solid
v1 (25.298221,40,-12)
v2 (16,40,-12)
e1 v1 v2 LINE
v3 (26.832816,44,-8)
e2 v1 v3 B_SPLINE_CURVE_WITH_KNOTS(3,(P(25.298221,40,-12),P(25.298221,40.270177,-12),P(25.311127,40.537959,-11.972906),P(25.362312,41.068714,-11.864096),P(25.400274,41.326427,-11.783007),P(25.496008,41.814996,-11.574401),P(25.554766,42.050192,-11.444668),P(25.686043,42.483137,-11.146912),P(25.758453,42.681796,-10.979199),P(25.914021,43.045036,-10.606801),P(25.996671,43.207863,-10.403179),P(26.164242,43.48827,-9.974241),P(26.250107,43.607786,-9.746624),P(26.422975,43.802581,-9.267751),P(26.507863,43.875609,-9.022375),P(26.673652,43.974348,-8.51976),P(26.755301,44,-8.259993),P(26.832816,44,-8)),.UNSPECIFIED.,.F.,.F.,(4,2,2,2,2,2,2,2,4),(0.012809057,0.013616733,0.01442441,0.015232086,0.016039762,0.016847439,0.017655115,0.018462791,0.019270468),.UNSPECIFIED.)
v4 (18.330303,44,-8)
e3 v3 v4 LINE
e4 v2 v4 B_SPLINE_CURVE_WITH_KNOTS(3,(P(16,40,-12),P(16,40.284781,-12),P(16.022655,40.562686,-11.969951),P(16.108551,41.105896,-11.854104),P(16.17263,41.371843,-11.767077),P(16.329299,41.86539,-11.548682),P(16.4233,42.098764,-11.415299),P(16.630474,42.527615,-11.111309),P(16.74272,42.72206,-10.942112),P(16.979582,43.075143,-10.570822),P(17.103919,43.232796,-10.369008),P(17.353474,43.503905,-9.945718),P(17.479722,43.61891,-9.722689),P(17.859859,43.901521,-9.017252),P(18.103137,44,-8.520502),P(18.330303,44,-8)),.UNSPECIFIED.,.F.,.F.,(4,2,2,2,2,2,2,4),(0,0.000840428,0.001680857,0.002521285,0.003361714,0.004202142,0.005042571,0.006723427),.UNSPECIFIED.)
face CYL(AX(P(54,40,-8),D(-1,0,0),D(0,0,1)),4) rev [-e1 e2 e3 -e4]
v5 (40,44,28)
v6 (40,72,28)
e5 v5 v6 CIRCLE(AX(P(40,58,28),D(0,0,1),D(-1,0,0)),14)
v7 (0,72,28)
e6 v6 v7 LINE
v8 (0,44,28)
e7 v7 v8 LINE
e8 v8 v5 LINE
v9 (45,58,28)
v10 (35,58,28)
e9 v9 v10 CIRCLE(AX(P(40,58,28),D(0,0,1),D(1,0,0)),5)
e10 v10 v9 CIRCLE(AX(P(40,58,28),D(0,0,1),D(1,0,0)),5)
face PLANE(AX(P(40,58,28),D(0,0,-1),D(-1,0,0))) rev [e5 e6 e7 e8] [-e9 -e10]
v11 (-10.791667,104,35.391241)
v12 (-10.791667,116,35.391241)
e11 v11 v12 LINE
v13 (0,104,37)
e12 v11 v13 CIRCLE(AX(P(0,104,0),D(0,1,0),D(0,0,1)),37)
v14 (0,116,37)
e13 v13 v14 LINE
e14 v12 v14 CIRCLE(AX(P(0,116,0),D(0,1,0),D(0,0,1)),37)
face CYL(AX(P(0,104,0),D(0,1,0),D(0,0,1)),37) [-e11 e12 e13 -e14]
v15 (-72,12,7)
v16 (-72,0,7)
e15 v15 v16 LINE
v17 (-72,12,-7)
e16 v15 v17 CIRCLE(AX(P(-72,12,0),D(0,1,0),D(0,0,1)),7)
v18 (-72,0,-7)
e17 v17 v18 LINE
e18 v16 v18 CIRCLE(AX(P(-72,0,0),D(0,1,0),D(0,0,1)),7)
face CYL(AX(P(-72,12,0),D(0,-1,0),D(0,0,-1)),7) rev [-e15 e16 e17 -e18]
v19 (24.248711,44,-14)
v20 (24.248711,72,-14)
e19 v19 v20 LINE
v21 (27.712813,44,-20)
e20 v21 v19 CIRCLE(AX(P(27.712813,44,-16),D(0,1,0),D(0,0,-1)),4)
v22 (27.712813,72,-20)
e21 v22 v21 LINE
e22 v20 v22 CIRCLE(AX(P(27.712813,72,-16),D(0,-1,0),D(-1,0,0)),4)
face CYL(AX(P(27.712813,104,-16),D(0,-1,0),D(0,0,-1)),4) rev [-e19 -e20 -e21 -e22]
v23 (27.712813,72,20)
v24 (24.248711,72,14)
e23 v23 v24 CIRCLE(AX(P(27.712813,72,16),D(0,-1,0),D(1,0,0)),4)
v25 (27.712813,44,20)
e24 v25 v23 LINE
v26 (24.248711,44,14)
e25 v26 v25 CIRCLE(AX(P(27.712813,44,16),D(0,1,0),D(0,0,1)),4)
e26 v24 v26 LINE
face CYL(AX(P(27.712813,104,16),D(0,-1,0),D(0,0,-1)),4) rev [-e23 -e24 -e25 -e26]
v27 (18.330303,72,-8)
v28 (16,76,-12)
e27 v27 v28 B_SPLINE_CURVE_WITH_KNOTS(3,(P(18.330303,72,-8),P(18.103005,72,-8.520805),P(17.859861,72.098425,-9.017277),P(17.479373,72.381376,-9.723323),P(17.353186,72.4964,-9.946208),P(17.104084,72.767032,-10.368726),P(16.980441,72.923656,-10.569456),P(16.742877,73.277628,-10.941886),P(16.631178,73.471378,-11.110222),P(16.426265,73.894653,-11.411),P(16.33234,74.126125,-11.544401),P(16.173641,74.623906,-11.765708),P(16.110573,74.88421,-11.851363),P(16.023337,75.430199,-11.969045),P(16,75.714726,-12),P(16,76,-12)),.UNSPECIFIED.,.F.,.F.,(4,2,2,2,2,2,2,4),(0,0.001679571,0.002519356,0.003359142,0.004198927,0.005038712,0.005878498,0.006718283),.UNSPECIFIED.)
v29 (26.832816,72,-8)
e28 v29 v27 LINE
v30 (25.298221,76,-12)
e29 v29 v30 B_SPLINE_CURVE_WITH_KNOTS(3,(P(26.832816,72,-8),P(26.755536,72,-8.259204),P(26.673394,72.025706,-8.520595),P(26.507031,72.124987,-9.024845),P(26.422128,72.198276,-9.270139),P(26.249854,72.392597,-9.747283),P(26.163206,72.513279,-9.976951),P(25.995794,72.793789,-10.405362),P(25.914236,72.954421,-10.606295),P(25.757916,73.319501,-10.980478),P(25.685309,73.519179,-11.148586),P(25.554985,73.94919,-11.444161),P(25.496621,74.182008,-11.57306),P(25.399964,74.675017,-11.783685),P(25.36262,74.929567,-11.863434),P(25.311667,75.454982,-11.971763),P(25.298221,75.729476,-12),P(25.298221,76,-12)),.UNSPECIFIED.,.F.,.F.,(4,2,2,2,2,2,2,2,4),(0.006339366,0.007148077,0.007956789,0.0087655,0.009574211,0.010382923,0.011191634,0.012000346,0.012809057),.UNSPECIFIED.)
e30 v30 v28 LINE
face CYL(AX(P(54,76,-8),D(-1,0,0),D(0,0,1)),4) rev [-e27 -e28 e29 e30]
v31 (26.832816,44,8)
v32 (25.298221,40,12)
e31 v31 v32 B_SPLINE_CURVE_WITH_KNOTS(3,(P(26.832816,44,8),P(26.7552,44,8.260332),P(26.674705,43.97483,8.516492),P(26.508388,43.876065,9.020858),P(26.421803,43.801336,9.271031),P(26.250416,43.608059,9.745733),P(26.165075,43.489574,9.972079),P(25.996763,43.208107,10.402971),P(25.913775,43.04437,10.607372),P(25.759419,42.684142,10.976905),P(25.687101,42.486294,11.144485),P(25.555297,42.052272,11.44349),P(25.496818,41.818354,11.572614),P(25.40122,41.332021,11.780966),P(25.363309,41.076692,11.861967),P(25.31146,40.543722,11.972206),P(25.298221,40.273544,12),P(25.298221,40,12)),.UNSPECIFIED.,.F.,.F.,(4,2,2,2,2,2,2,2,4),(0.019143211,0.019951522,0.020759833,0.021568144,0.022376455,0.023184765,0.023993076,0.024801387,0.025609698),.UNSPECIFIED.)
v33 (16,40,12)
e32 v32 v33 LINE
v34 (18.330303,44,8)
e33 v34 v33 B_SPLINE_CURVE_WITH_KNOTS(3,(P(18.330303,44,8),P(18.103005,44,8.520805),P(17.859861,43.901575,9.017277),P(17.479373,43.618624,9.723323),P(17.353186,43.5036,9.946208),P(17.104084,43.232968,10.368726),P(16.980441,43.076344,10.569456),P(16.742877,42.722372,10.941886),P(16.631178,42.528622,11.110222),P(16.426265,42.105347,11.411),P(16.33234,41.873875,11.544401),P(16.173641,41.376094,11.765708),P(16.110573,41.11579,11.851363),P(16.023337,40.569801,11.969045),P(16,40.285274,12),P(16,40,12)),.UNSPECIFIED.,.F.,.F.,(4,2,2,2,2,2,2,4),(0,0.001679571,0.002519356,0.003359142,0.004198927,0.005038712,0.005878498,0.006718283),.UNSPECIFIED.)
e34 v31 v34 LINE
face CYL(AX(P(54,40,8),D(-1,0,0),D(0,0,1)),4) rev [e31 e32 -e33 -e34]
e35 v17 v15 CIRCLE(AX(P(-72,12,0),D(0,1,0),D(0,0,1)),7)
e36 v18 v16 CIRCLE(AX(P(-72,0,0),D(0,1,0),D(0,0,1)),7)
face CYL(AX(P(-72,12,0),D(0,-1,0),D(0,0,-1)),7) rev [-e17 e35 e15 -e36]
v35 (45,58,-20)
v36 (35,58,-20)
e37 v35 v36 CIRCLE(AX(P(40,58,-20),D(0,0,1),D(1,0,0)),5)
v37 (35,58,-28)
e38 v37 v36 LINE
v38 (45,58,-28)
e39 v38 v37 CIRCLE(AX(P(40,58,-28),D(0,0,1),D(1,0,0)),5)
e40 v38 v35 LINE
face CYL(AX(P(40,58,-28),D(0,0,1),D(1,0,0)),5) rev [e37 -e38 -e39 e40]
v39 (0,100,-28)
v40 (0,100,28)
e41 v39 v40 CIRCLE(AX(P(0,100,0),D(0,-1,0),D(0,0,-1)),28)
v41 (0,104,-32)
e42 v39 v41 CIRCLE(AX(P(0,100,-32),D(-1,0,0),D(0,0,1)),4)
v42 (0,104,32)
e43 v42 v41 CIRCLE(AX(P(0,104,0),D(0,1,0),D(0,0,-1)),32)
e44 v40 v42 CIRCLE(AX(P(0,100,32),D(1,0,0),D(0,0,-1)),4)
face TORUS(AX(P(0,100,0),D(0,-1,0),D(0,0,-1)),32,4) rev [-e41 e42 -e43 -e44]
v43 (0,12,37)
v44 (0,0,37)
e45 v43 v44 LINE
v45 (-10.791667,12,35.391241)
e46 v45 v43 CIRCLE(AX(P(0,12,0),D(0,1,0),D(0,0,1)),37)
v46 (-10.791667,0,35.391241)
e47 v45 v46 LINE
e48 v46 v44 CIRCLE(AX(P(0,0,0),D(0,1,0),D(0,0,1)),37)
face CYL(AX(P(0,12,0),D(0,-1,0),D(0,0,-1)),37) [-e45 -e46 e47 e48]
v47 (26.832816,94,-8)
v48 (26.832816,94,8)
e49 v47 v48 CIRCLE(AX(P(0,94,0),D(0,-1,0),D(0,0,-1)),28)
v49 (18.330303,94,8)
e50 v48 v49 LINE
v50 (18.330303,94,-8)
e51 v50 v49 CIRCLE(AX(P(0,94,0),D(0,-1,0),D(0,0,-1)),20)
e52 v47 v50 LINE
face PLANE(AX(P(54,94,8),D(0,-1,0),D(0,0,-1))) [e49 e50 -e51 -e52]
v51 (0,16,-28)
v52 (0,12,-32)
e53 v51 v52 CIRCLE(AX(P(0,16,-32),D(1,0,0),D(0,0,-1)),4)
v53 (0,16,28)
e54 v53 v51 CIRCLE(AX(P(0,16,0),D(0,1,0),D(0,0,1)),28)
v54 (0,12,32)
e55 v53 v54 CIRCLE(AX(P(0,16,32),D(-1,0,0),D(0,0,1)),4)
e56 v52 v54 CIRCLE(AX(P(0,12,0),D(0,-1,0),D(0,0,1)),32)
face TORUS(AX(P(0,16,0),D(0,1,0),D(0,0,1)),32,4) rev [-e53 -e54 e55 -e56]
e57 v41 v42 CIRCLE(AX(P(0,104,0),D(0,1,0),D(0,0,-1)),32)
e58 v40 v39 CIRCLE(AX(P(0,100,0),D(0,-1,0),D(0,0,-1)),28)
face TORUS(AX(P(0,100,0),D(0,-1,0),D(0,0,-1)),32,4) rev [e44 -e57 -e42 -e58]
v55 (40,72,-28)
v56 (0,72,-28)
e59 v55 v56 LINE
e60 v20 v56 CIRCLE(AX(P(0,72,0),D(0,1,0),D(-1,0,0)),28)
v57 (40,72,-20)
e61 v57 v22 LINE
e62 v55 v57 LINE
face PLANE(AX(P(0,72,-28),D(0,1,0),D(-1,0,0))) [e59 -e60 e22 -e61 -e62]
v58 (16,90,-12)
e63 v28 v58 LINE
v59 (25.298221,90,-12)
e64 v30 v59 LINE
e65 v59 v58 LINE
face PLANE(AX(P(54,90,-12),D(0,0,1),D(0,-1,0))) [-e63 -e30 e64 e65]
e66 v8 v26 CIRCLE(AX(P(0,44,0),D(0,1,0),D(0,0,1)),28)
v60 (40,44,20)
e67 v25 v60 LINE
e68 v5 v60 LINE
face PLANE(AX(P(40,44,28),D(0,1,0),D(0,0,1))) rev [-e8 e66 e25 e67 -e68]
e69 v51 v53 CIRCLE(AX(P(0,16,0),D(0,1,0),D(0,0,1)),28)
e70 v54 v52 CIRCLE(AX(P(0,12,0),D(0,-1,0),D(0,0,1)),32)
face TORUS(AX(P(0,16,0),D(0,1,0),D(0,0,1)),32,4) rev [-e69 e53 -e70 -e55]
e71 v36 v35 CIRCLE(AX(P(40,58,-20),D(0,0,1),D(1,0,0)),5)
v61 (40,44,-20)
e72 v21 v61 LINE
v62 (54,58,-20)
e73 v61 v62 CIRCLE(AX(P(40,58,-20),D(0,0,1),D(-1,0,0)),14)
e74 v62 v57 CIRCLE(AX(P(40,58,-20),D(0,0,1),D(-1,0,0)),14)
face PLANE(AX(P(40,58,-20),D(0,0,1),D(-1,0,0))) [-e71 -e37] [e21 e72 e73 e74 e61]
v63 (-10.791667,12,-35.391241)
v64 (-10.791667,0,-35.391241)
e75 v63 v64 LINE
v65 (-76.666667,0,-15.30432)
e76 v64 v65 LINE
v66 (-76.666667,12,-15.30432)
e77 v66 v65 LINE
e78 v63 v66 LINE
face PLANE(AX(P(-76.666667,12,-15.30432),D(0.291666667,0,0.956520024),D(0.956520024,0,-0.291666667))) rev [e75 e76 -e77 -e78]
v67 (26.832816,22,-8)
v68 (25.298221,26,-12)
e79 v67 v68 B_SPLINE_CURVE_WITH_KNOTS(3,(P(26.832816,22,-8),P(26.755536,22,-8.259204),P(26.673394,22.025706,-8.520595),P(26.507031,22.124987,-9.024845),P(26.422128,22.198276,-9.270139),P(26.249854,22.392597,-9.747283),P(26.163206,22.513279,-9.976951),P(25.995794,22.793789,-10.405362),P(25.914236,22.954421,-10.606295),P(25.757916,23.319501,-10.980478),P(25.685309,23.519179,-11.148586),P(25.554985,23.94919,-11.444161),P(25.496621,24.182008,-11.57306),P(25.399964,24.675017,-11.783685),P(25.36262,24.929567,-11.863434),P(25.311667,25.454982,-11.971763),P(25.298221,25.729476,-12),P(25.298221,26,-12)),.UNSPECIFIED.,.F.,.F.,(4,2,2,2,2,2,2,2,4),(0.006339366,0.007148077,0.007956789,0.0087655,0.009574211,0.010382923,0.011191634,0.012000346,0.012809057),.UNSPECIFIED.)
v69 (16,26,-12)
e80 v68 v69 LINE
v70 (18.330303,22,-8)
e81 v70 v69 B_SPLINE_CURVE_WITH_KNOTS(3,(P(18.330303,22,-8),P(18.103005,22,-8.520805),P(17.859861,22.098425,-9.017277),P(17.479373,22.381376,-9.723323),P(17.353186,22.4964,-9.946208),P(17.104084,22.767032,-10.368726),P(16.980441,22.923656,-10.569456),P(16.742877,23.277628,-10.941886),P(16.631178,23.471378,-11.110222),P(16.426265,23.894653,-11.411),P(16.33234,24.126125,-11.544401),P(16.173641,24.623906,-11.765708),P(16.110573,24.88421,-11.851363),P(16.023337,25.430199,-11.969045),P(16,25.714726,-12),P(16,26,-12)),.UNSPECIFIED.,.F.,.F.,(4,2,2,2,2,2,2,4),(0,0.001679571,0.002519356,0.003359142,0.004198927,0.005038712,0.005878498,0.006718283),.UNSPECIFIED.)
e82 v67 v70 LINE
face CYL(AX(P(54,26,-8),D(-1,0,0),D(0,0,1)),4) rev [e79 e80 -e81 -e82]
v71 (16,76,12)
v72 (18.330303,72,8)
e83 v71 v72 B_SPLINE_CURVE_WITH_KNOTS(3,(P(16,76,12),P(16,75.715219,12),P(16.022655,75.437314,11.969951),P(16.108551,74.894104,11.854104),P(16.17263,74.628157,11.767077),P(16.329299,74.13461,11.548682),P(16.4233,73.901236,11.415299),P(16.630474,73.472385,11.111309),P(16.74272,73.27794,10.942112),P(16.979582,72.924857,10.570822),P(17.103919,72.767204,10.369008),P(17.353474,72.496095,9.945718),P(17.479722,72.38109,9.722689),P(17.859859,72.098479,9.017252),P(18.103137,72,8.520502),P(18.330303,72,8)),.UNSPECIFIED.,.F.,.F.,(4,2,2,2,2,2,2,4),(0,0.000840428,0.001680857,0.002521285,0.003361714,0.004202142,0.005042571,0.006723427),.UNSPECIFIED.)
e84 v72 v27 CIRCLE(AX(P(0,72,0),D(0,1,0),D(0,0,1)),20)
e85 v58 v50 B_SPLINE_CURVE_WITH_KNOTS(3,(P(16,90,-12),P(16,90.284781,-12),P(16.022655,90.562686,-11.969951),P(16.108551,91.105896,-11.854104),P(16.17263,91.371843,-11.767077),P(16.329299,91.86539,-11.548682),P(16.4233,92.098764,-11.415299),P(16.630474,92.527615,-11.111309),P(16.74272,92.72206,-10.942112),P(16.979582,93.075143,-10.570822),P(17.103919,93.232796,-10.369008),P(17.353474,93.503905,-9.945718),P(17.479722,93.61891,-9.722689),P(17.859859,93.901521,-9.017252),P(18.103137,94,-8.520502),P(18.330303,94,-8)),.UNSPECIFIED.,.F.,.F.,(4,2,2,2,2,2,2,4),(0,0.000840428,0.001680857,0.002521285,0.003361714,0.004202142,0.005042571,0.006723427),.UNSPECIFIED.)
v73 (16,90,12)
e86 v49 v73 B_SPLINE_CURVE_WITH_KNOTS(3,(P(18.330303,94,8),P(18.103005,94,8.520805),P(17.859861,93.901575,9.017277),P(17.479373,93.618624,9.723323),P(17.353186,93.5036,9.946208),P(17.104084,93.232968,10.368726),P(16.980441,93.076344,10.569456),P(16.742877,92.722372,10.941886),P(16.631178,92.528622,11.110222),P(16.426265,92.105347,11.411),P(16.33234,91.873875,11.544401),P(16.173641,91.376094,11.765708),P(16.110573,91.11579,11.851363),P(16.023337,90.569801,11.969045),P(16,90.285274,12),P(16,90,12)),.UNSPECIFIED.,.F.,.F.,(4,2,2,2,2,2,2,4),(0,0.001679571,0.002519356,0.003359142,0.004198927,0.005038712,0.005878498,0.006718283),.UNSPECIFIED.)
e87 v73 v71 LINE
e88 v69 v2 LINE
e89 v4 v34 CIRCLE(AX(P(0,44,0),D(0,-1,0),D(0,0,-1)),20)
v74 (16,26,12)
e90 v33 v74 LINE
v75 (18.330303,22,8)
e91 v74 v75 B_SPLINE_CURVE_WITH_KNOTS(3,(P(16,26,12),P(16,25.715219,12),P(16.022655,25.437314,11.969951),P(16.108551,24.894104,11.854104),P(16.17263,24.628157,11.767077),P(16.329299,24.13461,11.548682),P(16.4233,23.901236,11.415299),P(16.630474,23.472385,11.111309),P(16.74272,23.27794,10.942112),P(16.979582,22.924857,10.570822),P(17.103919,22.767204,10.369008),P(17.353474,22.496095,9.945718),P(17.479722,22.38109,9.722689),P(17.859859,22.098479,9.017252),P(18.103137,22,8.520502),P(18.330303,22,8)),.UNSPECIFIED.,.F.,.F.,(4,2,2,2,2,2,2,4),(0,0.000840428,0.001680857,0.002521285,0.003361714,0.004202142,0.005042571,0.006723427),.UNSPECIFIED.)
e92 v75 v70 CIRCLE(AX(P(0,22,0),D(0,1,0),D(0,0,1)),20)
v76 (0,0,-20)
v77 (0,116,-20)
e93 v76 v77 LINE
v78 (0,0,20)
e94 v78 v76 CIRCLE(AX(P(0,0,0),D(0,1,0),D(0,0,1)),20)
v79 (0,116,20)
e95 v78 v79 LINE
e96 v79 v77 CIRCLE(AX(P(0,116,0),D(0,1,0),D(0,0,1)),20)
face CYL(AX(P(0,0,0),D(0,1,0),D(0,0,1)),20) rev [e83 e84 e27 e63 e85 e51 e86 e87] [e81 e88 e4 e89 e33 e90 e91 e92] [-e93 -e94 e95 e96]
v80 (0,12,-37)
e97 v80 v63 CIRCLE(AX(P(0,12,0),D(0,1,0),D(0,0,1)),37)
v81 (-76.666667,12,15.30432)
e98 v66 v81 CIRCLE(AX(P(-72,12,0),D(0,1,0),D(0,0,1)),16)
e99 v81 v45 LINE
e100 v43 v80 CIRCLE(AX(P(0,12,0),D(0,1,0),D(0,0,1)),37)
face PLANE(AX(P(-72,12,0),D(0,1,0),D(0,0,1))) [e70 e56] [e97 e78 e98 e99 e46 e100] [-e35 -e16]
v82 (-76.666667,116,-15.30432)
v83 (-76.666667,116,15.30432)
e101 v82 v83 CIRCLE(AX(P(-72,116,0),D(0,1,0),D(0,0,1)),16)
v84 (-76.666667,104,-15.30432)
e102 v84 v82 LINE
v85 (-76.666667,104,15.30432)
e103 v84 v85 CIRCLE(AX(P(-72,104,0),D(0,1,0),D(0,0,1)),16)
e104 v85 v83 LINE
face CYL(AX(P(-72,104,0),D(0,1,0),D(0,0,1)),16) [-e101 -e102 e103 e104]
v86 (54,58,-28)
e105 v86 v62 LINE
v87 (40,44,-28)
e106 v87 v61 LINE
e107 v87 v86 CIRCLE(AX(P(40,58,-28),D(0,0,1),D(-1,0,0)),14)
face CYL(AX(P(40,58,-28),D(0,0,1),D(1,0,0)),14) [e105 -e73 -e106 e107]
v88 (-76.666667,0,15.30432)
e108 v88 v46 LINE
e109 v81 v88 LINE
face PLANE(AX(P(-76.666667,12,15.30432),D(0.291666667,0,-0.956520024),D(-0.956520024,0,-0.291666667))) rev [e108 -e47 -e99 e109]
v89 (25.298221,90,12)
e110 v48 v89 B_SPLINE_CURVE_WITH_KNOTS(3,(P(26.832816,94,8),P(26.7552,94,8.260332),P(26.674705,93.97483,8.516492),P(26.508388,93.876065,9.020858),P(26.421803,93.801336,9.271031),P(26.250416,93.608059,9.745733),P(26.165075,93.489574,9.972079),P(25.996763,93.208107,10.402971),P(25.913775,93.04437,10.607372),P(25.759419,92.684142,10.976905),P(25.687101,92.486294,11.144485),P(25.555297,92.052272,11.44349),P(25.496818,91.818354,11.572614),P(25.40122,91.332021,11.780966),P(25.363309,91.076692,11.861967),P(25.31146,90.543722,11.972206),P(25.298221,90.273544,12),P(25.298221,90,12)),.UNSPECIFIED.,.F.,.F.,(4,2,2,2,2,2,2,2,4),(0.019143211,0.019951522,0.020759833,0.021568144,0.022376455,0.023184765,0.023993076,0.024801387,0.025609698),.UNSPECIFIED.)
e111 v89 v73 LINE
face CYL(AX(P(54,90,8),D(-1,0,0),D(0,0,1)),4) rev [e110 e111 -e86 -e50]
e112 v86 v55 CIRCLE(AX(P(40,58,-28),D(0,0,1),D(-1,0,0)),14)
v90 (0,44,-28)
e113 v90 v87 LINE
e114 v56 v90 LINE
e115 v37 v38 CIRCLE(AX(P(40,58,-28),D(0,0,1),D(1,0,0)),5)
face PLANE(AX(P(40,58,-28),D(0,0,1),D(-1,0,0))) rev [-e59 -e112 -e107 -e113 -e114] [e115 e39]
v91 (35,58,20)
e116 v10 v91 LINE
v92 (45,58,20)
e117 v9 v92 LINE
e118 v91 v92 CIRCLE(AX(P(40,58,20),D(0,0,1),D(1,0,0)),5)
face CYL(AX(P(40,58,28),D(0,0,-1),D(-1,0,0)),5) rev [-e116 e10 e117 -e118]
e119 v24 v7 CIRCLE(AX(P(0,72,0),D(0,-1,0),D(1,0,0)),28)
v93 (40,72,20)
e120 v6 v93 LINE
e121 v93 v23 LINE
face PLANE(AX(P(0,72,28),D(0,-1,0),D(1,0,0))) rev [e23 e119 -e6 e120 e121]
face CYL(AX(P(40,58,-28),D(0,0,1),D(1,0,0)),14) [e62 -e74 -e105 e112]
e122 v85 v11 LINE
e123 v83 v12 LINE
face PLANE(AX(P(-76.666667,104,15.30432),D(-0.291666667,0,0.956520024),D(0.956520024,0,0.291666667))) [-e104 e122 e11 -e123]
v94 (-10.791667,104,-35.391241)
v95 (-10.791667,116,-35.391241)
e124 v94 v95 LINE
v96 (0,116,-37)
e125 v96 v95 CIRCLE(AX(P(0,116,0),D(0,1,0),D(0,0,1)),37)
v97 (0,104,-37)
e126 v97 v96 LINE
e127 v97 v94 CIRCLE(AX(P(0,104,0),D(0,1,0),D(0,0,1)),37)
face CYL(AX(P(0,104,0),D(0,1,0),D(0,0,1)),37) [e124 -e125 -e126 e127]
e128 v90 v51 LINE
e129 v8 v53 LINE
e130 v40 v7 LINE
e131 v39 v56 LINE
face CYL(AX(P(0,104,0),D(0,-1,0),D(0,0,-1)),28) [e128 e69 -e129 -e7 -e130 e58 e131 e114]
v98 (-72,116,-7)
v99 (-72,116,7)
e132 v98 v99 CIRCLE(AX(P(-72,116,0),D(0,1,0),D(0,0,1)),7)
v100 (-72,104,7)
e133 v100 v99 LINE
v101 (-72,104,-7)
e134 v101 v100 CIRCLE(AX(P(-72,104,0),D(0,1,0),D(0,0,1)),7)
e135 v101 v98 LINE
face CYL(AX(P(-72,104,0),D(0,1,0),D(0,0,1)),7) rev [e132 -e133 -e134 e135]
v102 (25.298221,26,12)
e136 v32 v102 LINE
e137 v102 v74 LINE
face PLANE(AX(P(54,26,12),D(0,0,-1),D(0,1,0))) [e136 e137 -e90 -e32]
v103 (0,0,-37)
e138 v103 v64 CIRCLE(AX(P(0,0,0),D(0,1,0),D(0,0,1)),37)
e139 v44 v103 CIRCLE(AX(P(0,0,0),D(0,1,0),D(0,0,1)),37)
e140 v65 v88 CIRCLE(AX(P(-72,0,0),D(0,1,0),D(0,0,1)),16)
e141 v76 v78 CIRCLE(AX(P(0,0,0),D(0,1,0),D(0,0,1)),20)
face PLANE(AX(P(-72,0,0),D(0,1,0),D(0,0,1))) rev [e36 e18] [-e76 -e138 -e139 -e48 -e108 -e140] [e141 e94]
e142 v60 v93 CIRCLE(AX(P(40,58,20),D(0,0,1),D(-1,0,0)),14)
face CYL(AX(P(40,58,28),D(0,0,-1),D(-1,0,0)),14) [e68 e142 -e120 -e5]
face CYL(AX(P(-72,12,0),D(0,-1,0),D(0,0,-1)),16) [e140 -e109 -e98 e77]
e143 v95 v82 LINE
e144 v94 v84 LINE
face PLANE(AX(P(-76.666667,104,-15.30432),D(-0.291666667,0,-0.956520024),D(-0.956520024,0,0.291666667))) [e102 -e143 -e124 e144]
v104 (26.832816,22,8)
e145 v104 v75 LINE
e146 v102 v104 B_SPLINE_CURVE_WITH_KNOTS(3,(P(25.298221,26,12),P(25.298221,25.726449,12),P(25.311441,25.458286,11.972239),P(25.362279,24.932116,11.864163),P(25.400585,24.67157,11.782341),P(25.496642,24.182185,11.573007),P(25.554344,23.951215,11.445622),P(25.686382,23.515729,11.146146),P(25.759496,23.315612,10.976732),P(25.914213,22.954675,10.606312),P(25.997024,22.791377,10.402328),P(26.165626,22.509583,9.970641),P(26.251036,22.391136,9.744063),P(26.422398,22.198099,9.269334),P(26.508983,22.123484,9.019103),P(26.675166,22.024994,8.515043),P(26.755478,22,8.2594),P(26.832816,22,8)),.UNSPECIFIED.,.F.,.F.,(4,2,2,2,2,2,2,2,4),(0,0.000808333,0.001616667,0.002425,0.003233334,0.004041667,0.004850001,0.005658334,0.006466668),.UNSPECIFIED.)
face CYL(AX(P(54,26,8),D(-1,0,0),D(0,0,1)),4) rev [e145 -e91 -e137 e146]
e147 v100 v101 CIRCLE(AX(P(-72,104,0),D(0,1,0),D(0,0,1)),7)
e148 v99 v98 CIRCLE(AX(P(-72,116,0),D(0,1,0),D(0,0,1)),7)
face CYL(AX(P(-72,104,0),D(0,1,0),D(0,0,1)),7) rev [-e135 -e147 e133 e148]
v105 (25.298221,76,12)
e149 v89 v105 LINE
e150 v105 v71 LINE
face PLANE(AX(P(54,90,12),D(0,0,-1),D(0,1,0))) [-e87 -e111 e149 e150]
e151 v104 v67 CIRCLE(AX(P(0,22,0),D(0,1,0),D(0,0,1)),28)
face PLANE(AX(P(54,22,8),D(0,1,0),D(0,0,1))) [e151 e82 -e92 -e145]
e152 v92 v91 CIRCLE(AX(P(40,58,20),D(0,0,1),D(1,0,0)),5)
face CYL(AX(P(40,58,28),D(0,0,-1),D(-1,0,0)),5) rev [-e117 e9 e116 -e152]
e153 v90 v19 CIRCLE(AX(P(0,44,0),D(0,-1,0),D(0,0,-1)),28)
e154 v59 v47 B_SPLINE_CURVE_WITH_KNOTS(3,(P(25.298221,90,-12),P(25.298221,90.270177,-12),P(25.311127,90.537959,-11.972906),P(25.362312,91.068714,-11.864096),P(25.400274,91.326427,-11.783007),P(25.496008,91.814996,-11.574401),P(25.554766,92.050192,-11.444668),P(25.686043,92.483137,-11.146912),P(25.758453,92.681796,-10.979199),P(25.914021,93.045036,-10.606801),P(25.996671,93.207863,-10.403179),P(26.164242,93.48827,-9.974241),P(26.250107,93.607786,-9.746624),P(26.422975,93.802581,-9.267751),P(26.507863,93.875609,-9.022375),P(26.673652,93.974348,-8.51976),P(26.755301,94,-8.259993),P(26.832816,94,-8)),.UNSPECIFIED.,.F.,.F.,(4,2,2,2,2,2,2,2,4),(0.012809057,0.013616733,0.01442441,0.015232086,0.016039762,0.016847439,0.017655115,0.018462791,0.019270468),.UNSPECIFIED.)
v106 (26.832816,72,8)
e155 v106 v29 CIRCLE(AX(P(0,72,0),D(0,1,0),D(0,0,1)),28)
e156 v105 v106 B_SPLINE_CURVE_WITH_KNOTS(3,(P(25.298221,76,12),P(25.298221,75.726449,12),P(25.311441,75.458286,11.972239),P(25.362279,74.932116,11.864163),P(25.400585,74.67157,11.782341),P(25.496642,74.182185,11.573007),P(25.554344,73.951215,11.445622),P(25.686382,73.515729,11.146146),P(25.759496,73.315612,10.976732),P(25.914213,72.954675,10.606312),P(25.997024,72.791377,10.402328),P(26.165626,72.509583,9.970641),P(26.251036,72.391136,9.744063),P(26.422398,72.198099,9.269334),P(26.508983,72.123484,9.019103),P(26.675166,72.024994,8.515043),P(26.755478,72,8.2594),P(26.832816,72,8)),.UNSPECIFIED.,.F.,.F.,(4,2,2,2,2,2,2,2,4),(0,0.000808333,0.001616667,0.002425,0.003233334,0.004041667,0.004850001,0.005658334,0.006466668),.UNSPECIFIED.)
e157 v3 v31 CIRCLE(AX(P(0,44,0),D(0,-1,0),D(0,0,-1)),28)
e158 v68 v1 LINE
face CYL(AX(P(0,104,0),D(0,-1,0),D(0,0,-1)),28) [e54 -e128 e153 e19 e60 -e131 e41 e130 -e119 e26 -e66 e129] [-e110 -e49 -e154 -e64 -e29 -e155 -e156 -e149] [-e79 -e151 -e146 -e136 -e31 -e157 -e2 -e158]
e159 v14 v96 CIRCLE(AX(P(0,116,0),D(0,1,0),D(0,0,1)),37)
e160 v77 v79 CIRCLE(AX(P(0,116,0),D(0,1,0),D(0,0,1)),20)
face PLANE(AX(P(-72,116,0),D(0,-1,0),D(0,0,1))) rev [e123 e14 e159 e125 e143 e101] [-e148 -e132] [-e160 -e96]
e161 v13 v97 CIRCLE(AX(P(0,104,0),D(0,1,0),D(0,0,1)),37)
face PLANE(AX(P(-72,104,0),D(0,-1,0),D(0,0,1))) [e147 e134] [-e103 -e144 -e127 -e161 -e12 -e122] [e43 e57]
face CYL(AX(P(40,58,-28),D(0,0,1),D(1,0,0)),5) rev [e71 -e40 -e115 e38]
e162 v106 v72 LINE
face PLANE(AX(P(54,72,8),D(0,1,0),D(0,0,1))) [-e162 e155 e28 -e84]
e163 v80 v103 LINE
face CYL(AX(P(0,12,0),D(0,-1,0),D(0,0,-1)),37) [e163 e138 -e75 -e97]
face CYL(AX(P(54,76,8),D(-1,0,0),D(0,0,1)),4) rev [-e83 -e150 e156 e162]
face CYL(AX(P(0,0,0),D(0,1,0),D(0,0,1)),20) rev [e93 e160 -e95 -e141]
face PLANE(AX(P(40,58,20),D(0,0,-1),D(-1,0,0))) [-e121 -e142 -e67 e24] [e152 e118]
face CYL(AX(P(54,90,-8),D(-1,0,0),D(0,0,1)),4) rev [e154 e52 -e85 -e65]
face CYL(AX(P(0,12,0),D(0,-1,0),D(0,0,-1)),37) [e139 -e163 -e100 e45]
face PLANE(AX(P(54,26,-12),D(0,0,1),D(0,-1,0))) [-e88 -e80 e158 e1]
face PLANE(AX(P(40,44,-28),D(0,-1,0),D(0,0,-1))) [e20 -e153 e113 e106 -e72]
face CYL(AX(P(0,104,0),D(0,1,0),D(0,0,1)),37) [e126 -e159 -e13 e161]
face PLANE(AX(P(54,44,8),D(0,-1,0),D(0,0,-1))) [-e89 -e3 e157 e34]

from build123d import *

# Parameters (mm, degrees)
LOWER_ARM_PROFILE_R    = 7
LOWER_ARM_PLATE_DEPTH  = 12
SLEEVE_PROFILE_56_R    = 28
SLEEVE_56_DEPTH        = 92
ARM_FILLETS_R4_R       = 4
TRUNNION_START         = 20
TRUNNION_LUG_PROFILE_R = 5
TRUNNION_LUG_DEPTH     = 8
LUG_FILLETS_R4_R       = 4
SLEEVE_WINDOWS_DEPTH   = 151.229823937
BORE_PROFILE_40_R      = 20
BORE_40_DEPTH          = 151.229823937


with BuildPart() as part:
    # Lower Arm Profile → Lower Arm Plate (new body)
    with BuildSketch(Plane(origin=(0, 0, 0), x_dir=(1, 0, 0), z_dir=(0, 1, 0))):
        with BuildLine():
            Line((-76.666666667, 15.304320378), (-10.791666667, 35.391240873))
            ThreePointArc((-10.791666667, 35.391240873), (37, 0), (-10.791666667, -35.391240873))
            Line((-10.791666667, -35.391240873), (-76.666666667, -15.304320378))
            ThreePointArc((-76.666666667, -15.304320378), (-88, 0), (-76.666666667, 15.304320378))
        make_face()
        with Locations(Location((-72, 0, 0), (0, 0, 270))):
            Circle(LOWER_ARM_PROFILE_R, mode=Mode.SUBTRACT)
    lower_arm_plate = extrude(amount=LOWER_ARM_PLATE_DEPTH)

    # Sleeve Profile Ø56 → Sleeve Ø56 (add)
    with BuildSketch(Plane(origin=(0, 12, 0), x_dir=(1, 0, 0), z_dir=(0, 1, 0))):
        with Locations(Location((0, 0, 0), (0, 0, 270))):
            Circle(SLEEVE_PROFILE_56_R)
    extrude(amount=SLEEVE_56_DEPTH)

    # Upper Arm Mirror: Lower Arm Plate across plane
    add(lower_arm_plate.mirror(Plane.ZX.offset(58)))

    # Arm Fillets R4
    arm_fillets_r4_edges = [part.edges().sort_by_distance(p)[0] for p in [
        (0, 12, -28),
        (0, 104, -28),
    ]]
    fillet(arm_fillets_r4_edges, radius=ARM_FILLETS_R4_R)

    # Trunnion Lug Profile → Trunnion Lug (add)
    with BuildSketch(Plane.XY.offset(TRUNNION_START)):
        with BuildLine():
            Line((0, 72), (40, 72))
            ThreePointArc((40, 72), (54, 58), (40, 44))
            Line((40, 44), (0, 44))
            Line((0, 44), (0, 72))
        make_face()
        with Locations((40, 58)):
            Circle(TRUNNION_LUG_PROFILE_R, mode=Mode.SUBTRACT)
    trunnion_lug = extrude(amount=TRUNNION_LUG_DEPTH)

    # Trunnion Lug Mirror: Trunnion Lug across plane
    add(trunnion_lug.mirror(Plane.XY))

    # Lug Fillets R4
    lug_fillets_r4_edges = [part.edges().sort_by_distance(p)[0] for p in [
        (19.595917942, 58, 20),
        (19.595917942, 58, -20),
    ]]
    fillet(lug_fillets_r4_edges, radius=LUG_FILLETS_R4_R)

    # Sleeve Window Profile → Sleeve Windows (cut, through all)
    with BuildSketch(Plane(origin=(0, 0, 0), x_dir=(0, 0, -1), z_dir=(1, 0, 0))):
        with BuildLine():
            Line((-8, 94), (8, 94))
            ThreePointArc((8, 94), (10.828427125, 92.828427125), (12, 90))
            Line((12, 90), (12, 76))
            ThreePointArc((12, 76), (10.828427125, 73.171572875), (8, 72))
            Line((8, 72), (-8, 72))
            ThreePointArc((-8, 72), (-10.828427125, 73.171572875), (-12, 76))
            Line((-12, 76), (-12, 90))
            ThreePointArc((-12, 90), (-10.828427125, 92.828427125), (-8, 94))
        make_face()
        with BuildLine():
            Line((-8, 22), (8, 22))
            ThreePointArc((8, 22), (10.828427125, 23.171572875), (12, 26))
            Line((12, 26), (12, 40))
            ThreePointArc((12, 40), (10.828427125, 42.828427125), (8, 44))
            Line((8, 44), (-8, 44))
            ThreePointArc((-8, 44), (-10.828427125, 42.828427125), (-12, 40))
            Line((-12, 40), (-12, 26))
            ThreePointArc((-12, 26), (-10.828427125, 23.171572875), (-8, 22))
        make_face()
    extrude(amount=SLEEVE_WINDOWS_DEPTH, mode=Mode.SUBTRACT)

    # Bore Profile Ø40 → Bore Ø40 (cut, through all)
    with BuildSketch(Plane(origin=(0, 116, 0), x_dir=(1, 0, 0), z_dir=(0, 1, 0))):
        with Locations(Location((0, 0, 0), (0, 0, 270))):
            Circle(BORE_PROFILE_40_R)
    extrude(amount=-BORE_40_DEPTH, mode=Mode.SUBTRACT)


solid = part.part
